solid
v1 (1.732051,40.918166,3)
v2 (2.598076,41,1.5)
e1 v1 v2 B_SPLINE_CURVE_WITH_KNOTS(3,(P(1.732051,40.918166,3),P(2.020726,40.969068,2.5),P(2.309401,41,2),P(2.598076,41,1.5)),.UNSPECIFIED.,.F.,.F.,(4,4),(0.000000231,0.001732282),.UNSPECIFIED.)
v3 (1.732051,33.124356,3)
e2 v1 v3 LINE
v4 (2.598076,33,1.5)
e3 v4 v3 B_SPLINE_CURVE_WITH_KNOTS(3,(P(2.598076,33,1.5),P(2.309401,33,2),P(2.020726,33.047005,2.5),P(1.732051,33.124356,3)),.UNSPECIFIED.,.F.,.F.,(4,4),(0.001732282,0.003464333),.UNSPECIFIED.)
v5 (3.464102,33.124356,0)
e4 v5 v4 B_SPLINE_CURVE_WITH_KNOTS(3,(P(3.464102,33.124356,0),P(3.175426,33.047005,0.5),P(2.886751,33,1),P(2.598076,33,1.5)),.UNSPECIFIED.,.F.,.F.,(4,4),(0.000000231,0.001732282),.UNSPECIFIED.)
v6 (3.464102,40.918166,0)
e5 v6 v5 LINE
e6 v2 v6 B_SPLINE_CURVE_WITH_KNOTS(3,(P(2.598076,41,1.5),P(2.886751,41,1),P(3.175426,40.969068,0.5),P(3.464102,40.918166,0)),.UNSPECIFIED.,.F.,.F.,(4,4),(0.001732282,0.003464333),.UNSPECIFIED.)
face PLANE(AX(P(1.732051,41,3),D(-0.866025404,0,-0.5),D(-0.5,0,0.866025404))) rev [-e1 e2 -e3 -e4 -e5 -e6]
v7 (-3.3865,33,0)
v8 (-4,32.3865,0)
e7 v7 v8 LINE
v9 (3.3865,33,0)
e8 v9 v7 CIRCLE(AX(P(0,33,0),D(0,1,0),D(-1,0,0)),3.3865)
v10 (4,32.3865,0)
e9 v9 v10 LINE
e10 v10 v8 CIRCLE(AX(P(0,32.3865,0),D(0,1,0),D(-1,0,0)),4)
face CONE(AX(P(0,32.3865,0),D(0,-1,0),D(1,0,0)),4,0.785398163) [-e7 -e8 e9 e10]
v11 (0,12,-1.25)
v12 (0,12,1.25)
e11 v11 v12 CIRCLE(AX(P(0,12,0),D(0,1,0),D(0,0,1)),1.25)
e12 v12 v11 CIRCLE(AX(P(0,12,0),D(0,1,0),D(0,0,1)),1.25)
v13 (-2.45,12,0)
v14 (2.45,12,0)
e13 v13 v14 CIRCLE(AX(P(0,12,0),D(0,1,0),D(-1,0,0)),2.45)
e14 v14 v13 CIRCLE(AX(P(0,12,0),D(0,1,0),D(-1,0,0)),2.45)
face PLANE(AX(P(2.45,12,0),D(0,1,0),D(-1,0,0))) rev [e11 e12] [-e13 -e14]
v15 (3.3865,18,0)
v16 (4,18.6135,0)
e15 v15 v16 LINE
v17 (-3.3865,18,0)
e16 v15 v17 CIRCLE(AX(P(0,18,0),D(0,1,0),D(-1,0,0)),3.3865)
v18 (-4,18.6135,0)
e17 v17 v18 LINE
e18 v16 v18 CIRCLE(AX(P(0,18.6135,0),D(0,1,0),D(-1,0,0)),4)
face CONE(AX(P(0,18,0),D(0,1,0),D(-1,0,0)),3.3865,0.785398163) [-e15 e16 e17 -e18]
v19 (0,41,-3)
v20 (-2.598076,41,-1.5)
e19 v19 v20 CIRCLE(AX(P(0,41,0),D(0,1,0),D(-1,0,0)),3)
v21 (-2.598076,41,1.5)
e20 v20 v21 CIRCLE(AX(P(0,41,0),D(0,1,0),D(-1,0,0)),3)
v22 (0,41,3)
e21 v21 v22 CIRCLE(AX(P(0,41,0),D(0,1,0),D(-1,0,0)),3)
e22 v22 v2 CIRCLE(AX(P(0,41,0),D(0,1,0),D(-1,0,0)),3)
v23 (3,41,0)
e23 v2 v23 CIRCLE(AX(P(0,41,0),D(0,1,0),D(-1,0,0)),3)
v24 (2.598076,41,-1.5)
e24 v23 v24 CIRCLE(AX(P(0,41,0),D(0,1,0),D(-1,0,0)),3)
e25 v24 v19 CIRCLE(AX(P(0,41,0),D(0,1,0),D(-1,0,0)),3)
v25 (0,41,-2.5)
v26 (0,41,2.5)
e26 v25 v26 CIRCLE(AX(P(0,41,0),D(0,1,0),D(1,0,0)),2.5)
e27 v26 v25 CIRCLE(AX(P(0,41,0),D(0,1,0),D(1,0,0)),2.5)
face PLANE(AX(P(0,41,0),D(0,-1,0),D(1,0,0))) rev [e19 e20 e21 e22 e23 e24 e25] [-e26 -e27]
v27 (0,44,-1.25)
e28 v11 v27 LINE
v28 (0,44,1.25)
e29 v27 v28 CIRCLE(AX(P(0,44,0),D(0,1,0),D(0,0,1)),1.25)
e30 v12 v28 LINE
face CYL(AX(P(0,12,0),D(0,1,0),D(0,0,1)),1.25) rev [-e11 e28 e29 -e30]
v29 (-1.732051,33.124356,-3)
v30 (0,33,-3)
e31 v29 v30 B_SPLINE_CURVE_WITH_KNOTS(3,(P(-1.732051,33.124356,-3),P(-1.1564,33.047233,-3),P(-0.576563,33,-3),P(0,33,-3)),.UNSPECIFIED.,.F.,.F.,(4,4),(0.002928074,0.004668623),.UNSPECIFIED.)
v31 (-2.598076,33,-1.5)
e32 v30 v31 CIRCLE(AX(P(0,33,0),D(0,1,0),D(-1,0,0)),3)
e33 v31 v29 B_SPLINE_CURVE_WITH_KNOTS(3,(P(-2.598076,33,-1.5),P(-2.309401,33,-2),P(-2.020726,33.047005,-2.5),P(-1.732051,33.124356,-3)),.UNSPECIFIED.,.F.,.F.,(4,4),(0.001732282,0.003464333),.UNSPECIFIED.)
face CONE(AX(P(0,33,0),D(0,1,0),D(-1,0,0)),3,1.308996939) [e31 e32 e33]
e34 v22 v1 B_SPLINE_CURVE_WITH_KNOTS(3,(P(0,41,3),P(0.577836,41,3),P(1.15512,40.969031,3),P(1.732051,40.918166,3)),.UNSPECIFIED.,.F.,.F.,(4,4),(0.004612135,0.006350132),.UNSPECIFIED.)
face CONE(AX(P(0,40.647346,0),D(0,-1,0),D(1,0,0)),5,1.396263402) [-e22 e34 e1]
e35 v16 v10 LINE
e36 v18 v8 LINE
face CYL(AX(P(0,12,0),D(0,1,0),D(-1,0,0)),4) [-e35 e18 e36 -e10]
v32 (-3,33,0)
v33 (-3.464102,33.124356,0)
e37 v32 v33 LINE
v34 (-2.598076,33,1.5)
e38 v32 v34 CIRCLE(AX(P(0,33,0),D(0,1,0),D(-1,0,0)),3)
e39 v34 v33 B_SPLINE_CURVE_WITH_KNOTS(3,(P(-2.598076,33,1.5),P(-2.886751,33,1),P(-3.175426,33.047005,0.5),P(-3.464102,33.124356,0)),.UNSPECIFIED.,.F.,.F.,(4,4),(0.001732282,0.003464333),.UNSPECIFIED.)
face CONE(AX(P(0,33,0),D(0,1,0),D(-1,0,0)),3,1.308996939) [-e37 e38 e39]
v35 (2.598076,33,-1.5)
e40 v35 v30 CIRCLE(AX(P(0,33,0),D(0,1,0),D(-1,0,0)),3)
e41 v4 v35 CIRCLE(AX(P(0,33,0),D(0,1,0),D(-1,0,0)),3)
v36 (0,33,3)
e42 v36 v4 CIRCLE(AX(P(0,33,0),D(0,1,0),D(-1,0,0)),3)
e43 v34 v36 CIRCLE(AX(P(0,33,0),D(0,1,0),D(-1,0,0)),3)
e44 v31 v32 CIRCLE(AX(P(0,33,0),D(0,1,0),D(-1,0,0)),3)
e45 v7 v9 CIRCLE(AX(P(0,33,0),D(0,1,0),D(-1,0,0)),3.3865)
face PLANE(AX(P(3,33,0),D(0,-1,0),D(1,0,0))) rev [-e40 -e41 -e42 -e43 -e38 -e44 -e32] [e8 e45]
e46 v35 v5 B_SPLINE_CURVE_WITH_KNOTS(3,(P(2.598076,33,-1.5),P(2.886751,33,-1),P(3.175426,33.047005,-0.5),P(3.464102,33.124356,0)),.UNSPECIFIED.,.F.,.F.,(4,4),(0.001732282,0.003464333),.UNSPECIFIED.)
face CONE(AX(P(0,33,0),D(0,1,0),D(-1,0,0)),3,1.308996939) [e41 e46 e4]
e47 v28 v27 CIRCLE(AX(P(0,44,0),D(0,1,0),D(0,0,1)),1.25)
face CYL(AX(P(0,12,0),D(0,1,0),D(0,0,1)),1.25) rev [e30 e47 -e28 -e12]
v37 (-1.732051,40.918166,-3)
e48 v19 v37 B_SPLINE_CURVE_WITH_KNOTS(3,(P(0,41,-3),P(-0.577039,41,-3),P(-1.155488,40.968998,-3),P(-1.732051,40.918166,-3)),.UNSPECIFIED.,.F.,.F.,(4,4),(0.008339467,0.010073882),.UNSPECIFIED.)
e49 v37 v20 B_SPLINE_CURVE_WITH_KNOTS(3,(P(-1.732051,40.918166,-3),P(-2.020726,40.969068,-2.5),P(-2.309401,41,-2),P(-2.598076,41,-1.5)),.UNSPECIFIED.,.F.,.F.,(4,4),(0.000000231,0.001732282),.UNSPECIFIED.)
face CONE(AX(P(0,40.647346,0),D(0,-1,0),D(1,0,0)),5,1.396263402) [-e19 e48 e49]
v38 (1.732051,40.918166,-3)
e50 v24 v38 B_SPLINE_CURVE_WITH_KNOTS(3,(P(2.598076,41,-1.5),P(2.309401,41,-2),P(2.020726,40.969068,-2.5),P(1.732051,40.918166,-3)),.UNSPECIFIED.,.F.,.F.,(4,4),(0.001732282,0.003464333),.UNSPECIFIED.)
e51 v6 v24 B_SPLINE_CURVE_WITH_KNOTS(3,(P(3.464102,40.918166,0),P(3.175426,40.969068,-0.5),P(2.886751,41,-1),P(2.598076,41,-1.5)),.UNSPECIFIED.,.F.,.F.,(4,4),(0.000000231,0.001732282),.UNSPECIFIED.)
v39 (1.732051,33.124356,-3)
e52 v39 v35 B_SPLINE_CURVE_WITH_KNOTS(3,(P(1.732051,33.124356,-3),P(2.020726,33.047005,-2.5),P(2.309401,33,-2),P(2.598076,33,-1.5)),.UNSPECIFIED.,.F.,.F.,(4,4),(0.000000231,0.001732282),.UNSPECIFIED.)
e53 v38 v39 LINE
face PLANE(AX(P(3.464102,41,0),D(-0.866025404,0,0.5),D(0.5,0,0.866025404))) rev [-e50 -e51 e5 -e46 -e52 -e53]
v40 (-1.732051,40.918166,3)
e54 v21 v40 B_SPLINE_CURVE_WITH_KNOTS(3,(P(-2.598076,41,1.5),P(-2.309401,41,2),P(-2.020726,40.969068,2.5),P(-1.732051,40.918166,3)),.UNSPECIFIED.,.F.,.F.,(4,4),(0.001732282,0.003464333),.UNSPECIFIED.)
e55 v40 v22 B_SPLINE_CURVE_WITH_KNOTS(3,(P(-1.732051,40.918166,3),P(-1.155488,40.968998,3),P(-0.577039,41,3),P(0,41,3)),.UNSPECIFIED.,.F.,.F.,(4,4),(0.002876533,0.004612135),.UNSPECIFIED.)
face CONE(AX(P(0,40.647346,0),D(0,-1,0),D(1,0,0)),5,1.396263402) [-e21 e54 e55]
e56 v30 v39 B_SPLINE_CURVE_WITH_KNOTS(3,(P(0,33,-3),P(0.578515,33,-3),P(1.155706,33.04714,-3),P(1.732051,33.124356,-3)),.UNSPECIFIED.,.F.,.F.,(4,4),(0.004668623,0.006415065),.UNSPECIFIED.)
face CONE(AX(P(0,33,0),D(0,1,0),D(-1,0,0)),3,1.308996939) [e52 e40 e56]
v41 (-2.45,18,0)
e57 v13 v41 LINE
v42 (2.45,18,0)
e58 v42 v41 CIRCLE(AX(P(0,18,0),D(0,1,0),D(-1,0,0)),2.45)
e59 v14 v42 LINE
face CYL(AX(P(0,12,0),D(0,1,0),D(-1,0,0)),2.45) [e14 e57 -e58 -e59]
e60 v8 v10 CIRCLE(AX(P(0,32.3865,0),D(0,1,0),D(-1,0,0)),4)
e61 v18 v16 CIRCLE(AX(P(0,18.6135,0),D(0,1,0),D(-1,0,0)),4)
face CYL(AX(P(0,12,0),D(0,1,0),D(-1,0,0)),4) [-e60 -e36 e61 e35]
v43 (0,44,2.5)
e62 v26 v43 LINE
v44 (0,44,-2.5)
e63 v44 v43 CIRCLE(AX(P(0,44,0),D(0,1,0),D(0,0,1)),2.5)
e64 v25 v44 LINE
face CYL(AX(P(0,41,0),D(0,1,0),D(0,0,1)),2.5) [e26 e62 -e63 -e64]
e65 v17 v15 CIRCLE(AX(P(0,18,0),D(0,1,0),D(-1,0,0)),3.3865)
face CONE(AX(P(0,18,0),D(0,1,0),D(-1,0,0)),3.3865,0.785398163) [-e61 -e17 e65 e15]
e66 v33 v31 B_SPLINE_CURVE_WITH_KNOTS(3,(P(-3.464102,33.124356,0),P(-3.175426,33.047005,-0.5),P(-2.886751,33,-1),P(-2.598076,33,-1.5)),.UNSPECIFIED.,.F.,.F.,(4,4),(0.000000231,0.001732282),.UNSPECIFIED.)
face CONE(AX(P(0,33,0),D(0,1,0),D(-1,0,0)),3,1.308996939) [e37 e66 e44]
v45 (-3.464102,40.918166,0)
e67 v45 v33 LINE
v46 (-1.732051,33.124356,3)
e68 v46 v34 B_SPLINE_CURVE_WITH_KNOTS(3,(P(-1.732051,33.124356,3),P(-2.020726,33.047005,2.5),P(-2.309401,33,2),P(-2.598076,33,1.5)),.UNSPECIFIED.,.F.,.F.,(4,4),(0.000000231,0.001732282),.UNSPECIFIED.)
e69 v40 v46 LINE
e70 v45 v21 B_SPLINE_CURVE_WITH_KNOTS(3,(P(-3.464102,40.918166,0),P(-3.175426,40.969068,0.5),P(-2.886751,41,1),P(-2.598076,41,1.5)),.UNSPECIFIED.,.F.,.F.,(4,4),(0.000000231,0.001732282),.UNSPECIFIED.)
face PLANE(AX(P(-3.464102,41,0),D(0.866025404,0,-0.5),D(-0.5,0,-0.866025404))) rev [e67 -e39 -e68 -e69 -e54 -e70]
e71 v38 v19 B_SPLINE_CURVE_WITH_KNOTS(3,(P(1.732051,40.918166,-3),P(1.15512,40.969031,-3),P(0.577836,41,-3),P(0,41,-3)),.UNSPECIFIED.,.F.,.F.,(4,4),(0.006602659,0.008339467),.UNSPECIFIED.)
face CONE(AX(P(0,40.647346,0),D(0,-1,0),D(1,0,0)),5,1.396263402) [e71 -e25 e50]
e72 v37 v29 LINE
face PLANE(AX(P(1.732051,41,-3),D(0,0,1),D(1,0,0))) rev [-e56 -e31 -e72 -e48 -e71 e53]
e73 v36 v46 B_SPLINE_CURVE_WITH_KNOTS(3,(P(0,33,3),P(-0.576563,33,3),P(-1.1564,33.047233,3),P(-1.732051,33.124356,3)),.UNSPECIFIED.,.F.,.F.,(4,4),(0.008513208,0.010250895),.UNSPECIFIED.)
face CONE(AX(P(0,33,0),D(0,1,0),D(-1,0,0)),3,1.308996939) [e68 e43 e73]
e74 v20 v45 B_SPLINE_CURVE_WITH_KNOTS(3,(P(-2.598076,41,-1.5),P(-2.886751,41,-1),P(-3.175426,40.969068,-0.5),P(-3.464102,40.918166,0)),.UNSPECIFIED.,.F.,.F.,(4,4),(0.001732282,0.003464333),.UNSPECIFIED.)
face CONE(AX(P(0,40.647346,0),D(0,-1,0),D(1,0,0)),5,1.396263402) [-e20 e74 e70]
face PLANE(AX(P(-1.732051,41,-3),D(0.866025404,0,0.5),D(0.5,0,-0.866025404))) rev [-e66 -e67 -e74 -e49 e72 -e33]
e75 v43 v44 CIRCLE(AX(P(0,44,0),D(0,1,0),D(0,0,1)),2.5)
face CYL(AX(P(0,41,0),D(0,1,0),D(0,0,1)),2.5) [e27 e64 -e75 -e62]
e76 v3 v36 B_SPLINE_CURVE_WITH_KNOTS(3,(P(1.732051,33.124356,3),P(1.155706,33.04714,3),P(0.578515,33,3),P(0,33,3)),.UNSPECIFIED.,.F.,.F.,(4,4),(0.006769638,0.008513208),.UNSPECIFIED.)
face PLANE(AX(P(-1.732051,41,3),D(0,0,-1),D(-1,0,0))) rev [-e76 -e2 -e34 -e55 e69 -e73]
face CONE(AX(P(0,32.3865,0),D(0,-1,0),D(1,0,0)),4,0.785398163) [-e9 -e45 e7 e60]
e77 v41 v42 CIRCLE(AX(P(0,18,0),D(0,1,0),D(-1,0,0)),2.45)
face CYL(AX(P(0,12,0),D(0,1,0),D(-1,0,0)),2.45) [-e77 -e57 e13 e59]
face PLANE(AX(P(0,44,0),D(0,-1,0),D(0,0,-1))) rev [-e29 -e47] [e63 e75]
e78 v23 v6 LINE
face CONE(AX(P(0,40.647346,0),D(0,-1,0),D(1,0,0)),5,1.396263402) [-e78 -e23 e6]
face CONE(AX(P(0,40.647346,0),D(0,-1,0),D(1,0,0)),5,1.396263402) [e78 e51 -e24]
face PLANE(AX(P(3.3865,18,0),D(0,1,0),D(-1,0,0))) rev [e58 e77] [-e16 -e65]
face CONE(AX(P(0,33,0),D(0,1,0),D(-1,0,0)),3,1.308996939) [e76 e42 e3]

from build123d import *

# Parameters (mm, degrees)
SKETCH_2_R          = 6
CUT_EXTRUDE_1_DEPTH = 8
SKETCH_3_W          = 2.5
SKETCH_3_H          = 3
SKETCH_4_W          = 1.25
SKETCH_4_H          = 32


with BuildPart() as part:
    # 草图1 → 旋转1 (revolve)
    with BuildSketch(Plane.XY, mode=Mode.PRIVATE) as revolve_1_sk:
        Polygon((0, 41), (3, 41), (5, 40.647346039), (5, 33.535898385), (3, 33), (3.3865, 33), (4, 32.3865), (4, 18.6135), (3.3865, 18), (2.45, 18), (2.45, 12), (0, 12), align=None)
    revolve(revolve_1_sk.sketch.rotate(Axis((0, 12, 0), (0, 1, 0)), 180), axis=Axis((0, 12, 0), (0, 1, 0)))

    # 草图2 → 切除-拉伸1 (cut)
    with BuildSketch(Plane(origin=(0, 33, 0), x_dir=(1, 0, 0), z_dir=(0, 1, 0))):
        Circle(SKETCH_2_R)
        Polygon((-3.464101615, 0), (-1.732050808, -3), (1.732050808, -3), (3.464101615, 0), (1.732050808, 3), (-1.732050808, 3), align=None, mode=Mode.SUBTRACT)
    extrude(amount=CUT_EXTRUDE_1_DEPTH, mode=Mode.SUBTRACT)

    # 草图3 → 旋转2 (revolve)
    with BuildSketch(Plane.XY, mode=Mode.PRIVATE) as revolve_2_sk:
        with Locations((1.25, 42.5)):
            Rectangle(SKETCH_3_W, SKETCH_3_H)
    revolve(revolve_2_sk.sketch.rotate(Axis((0, 41, 0), (0, 1, 0)), 270), axis=Axis((0, 41, 0), (0, 1, 0)))

    # 草图4 → 切除-旋转1 (revolve, cut)
    with BuildSketch(Plane.XY, mode=Mode.PRIVATE) as cut_revolve_1_sk:
        with Locations((0.625, 28)):
            Rectangle(SKETCH_4_W, SKETCH_4_H)
    revolve(cut_revolve_1_sk.sketch.rotate(Axis((0, 12, 0), (0, 1, 0)), 270), axis=Axis((0, 12, 0), (0, 1, 0)), mode=Mode.SUBTRACT)


solid = part.part
